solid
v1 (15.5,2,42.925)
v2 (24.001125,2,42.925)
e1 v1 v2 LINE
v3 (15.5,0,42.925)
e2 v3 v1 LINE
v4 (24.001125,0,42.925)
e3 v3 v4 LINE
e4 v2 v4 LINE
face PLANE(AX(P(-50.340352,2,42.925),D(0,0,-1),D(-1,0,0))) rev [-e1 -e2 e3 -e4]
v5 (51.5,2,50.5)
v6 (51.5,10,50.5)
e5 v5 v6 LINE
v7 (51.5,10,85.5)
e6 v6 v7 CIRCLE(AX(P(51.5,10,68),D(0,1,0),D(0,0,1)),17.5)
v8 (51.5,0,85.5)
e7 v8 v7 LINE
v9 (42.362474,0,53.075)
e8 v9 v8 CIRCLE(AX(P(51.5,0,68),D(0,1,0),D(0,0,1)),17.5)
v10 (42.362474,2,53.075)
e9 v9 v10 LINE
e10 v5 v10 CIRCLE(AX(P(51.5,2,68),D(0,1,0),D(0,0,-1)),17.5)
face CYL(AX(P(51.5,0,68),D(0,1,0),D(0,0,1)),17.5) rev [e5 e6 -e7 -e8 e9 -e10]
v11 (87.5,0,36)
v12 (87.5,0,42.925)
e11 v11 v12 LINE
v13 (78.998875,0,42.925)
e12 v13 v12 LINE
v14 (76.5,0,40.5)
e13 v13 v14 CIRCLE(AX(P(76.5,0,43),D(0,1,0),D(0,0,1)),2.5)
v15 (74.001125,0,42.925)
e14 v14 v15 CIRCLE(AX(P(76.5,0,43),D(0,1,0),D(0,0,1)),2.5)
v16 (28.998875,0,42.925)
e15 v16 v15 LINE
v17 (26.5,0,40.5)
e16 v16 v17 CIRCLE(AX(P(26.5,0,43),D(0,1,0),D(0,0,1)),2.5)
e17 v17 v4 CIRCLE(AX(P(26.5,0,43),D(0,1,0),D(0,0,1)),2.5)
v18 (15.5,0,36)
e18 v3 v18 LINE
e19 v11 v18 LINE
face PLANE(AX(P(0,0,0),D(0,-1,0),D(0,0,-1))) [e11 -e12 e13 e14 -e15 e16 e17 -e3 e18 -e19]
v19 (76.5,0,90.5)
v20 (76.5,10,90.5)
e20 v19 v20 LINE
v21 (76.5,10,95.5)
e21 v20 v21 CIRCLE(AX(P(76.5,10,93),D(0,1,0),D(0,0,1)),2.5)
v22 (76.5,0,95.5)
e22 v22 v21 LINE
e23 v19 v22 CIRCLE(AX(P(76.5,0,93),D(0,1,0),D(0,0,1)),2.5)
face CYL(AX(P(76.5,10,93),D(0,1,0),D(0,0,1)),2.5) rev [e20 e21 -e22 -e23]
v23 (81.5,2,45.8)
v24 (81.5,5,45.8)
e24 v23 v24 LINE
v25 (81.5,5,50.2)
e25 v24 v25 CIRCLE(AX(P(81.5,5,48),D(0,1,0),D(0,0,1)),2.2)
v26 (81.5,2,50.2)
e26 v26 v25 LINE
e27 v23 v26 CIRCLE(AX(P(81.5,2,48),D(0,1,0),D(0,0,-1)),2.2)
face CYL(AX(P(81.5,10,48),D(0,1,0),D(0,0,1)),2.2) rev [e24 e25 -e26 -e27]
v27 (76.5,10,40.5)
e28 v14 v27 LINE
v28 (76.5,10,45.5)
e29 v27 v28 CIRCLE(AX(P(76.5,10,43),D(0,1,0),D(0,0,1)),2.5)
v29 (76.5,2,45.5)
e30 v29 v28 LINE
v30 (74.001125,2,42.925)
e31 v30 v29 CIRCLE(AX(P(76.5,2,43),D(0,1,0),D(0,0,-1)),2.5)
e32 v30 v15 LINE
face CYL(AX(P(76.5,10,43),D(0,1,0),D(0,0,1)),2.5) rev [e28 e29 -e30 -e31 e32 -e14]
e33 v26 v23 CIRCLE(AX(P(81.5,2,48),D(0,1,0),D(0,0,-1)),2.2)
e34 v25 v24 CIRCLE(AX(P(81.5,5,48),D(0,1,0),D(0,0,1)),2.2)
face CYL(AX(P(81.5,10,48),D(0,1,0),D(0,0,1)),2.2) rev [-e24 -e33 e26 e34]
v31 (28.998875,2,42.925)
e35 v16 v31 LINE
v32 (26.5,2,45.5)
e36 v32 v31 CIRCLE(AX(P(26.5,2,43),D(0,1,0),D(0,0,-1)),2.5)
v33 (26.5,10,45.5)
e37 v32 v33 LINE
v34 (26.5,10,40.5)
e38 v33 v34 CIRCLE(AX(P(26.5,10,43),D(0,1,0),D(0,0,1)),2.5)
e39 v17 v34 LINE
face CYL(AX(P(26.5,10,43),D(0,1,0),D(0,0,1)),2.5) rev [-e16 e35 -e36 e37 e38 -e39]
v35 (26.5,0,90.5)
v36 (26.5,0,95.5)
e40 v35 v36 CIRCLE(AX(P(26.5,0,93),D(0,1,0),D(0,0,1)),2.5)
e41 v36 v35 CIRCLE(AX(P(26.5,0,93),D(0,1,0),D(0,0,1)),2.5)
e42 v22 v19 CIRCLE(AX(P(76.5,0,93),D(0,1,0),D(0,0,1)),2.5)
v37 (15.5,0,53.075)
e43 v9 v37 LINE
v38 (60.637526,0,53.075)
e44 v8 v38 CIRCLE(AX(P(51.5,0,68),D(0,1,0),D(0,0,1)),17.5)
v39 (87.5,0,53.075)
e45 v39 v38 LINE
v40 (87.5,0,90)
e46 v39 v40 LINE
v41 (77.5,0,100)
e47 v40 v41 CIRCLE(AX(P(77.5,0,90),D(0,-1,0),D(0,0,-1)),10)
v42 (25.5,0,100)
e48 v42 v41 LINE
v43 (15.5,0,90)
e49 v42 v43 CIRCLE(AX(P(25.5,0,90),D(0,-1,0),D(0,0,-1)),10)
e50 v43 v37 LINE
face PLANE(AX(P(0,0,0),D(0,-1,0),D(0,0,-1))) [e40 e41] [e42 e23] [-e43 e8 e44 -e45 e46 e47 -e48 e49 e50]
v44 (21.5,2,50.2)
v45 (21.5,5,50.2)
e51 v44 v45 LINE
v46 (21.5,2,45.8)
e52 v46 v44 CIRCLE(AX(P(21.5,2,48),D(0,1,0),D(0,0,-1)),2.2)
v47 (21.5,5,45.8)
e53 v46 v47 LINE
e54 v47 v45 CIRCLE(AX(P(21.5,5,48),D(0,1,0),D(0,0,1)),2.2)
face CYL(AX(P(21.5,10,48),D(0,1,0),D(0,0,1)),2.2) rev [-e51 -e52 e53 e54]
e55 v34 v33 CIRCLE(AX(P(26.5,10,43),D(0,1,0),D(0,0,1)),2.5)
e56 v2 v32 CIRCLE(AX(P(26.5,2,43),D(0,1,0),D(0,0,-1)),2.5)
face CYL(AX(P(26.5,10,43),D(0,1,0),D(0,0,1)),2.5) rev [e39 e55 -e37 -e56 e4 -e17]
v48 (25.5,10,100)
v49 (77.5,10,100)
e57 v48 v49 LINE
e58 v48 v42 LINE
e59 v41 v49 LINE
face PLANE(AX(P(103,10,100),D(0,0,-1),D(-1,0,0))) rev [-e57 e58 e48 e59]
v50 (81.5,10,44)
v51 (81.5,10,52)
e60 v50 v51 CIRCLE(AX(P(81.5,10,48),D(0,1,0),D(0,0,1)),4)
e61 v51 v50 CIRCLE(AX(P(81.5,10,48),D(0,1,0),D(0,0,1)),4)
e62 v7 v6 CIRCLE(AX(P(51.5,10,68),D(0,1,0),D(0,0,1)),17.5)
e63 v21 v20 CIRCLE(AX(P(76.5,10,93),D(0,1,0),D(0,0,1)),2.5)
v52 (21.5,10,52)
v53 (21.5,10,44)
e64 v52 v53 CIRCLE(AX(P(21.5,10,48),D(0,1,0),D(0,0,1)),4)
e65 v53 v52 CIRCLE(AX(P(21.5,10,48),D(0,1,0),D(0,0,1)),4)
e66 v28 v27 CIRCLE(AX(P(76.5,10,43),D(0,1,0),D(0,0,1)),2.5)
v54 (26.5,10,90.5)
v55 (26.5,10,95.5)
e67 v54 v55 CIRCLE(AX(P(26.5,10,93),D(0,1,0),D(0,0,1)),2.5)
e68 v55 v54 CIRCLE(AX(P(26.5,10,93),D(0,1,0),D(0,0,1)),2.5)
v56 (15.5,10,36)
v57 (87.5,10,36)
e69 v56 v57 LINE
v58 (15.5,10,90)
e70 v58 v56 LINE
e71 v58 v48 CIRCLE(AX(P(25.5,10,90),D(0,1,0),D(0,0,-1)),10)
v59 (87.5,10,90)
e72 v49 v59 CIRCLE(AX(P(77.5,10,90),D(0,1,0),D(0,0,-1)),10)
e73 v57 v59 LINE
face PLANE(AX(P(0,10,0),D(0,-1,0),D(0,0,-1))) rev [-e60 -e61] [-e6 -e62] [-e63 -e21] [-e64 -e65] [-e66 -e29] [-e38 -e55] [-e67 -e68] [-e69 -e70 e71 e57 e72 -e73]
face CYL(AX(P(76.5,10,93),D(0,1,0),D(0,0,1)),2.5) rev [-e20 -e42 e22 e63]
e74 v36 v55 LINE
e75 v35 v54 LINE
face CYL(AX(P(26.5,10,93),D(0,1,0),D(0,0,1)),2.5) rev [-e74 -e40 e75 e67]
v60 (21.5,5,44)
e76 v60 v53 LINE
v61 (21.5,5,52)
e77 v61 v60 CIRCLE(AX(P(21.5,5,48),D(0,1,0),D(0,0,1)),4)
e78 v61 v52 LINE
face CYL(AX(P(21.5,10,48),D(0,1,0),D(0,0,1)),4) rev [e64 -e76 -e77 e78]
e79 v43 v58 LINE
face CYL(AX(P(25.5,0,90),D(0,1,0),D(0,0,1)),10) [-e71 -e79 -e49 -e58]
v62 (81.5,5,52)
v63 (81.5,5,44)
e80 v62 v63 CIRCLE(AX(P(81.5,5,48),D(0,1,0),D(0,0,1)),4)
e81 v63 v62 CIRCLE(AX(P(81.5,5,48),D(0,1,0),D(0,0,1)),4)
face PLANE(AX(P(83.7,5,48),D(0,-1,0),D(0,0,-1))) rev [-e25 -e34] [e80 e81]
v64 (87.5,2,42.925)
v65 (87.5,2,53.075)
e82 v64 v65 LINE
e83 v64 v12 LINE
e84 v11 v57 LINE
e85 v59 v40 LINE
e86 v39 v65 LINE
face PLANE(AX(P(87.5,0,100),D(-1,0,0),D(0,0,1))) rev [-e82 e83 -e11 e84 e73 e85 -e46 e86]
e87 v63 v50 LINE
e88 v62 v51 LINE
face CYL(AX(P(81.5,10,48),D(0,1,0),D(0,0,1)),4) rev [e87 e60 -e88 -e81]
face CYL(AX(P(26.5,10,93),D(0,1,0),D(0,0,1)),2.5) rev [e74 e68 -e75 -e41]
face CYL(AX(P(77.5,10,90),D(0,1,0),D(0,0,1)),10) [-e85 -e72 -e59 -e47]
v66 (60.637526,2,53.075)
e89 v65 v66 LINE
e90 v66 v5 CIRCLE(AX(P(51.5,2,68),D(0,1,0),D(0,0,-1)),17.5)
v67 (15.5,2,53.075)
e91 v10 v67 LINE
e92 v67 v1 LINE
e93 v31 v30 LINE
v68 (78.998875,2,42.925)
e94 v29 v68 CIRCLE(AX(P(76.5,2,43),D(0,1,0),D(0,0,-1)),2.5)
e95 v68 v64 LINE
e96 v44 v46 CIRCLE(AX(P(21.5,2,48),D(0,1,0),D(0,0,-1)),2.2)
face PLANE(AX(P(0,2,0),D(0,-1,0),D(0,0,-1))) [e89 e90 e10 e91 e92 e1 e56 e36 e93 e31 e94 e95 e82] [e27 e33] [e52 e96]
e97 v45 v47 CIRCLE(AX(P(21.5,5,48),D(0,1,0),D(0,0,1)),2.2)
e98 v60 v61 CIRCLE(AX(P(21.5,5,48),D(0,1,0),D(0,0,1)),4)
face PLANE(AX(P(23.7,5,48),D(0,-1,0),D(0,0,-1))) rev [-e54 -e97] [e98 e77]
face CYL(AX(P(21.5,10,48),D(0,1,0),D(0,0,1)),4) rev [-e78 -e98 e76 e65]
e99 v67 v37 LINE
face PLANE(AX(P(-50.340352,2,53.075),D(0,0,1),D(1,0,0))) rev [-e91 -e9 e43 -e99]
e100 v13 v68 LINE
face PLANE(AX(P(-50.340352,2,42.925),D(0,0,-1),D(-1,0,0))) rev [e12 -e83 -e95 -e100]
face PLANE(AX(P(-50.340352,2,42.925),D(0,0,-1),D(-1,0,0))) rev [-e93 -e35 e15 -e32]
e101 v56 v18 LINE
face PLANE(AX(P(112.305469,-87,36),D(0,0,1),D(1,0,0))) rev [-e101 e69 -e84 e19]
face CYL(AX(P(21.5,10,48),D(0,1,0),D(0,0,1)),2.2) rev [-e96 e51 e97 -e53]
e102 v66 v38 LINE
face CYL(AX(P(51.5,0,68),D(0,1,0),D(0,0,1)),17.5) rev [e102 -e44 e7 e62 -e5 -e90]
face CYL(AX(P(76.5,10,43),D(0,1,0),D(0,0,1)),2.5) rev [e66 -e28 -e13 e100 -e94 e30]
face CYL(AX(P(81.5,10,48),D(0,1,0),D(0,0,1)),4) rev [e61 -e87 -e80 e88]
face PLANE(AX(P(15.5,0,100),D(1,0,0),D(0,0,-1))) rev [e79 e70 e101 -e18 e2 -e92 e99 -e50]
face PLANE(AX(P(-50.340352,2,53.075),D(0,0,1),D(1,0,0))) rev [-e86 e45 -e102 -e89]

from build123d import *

# Parameters (mm, degrees)
SKETCH_1_W                = 103
SKETCH_1_H                = 100
EXTRUDE_1_DEPTH           = 10
SKETCH_9_W                = 15.5
SKETCH_9_H                = 88
CUT_EXTRUDE_4_DEPTH       = 144.906219463
HOLE_WIZARD_6_5_6_5_1_D   = 6.5
SKETCH_12_R               = 17.5
CUT_EXTRUDE_5_DEPTH       = 144.906219463
FILLET_1_R                = 10
HOLE_WIZARD_5_0_5_1_D     = 5
HOLE_WIZARD_5_0_5_1_DEPTH = 10
HOLE_WIZARD_5_0_5_1_TIP   = 1.502151548
FILLET_2_R                = 2
SKETCH_20_W               = 140.430498758
SKETCH_20_H               = 45.630669844
CUT_EXTRUDE_6_DEPTH       = 97
HOLE_WIZARD_1_D           = 4.4
HOLE_WIZARD_1_CBORE_D     = 8
HOLE_WIZARD_1_CBORE_DEPTH = 5
HOLE_WIZARD_M6_2_D        = 5
SKETCH_28_W               = 143.680703706
SKETCH_28_H               = 10.15
CUT_EXTRUDE_7_DEPTH       = 2


with BuildPart() as part:
    # 草图1 → 凸台-拉伸1 (new body)
    with BuildSketch(Plane(origin=(0, 0, 0), x_dir=(1, 0, 0), z_dir=(0, 1, 0))):
        with Locations((51.5, -50)):
            Rectangle(SKETCH_1_W, SKETCH_1_H)
    extrude(amount=EXTRUDE_1_DEPTH)

    # 草图9 → 切除-拉伸4 (cut, through all)
    with BuildSketch(Plane(origin=(0, 10, 0), x_dir=(1, 0, 0), z_dir=(0, 1, 0))):
        with Locations((7.75, -56)):
            Rectangle(SKETCH_9_W, SKETCH_9_H)
        with Locations((95.25, -56)):
            Rectangle(SKETCH_9_W, SKETCH_9_H)
    extrude(amount=-CUT_EXTRUDE_4_DEPTH, mode=Mode.SUBTRACT)

    # Ø6.5 (6.5) 直径孔1 (through all)
    with Locations(Plane.XY.offset(12)):
        with Locations((6, 5), (97, 5)):
            Hole(HOLE_WIZARD_6_5_6_5_1_D / 2)

    # 草图12 → 切除-拉伸5 (cut, through all)
    with BuildSketch(Plane(origin=(0, 10, 0), x_dir=(1, 0, 0), z_dir=(0, 1, 0))):
        with Locations(Location((51.5, -68, 0), (0, 0, 270))):
            Circle(SKETCH_12_R)
    extrude(amount=-CUT_EXTRUDE_5_DEPTH, mode=Mode.SUBTRACT)

    # 圆角1
    fillet_1_edges = [part.edges().sort_by_distance(p)[0] for p in [
        (15.5, 5, 100),
        (87.5, 5, 100),
    ]]
    fillet(fillet_1_edges, radius=FILLET_1_R)

    # Ø5.0 (5) 直径孔1
    with Locations(Plane(origin=(0, 0, 0), x_dir=(-1, 0, 0), z_dir=(0, 0, -1))):
        with Locations((-71.5, 5), (-31.5, 5)):
            Hole(HOLE_WIZARD_5_0_5_1_D / 2, depth=HOLE_WIZARD_5_0_5_1_DEPTH)
            with Locations((0, 0, -(HOLE_WIZARD_5_0_5_1_DEPTH + HOLE_WIZARD_5_0_5_1_TIP / 2))):  # 118° drill point
                Cone(0, HOLE_WIZARD_5_0_5_1_D / 2, HOLE_WIZARD_5_0_5_1_TIP, mode=Mode.SUBTRACT)

    # 圆角2
    fillet_2_edges = [part.edges().sort_by_distance(p)[0] for p in [
        (15.5, 5, 12),
        (87.5, 5, 12),
    ]]
    fillet(fillet_2_edges, radius=FILLET_2_R)

    # 草图20 → 切除-拉伸6 (cut)
    with BuildSketch(Plane(origin=(0, 10, 0), x_dir=(1, 0, 0), z_dir=(0, 1, 0))):
        with Locations((42.090220098, -13.184665078)):
            Rectangle(SKETCH_20_W, SKETCH_20_H)
    extrude(amount=-CUT_EXTRUDE_6_DEPTH, mode=Mode.SUBTRACT)

    # 打孔尺寸(%根据)内六角圆柱头螺钉的类型1 (through all)
    with Locations(Plane(origin=(0, 10, 0), x_dir=(1, 0, 0), z_dir=(0, 1, 0))):
        with Locations((21.5, -48), (81.5, -48)):
            CounterBoreHole(HOLE_WIZARD_1_D / 2, HOLE_WIZARD_1_CBORE_D / 2, HOLE_WIZARD_1_CBORE_DEPTH)

    # M6 螺纹孔2 (through all)
    with Locations(Plane(origin=(0, 10, 0), x_dir=(1, 0, 0), z_dir=(0, 1, 0))):
        with Locations((26.5, -43), (26.5, -93), (76.5, -93), (76.5, -43)):
            Hole(HOLE_WIZARD_M6_2_D / 2)

    # 草图28 → 切除-拉伸7 (cut)
    with BuildSketch(Plane.XZ):
        with Locations((21.5, 48)):
            Rectangle(SKETCH_28_W, SKETCH_28_H)
    extrude(amount=-CUT_EXTRUDE_7_DEPTH, mode=Mode.SUBTRACT)


solid = part.part
